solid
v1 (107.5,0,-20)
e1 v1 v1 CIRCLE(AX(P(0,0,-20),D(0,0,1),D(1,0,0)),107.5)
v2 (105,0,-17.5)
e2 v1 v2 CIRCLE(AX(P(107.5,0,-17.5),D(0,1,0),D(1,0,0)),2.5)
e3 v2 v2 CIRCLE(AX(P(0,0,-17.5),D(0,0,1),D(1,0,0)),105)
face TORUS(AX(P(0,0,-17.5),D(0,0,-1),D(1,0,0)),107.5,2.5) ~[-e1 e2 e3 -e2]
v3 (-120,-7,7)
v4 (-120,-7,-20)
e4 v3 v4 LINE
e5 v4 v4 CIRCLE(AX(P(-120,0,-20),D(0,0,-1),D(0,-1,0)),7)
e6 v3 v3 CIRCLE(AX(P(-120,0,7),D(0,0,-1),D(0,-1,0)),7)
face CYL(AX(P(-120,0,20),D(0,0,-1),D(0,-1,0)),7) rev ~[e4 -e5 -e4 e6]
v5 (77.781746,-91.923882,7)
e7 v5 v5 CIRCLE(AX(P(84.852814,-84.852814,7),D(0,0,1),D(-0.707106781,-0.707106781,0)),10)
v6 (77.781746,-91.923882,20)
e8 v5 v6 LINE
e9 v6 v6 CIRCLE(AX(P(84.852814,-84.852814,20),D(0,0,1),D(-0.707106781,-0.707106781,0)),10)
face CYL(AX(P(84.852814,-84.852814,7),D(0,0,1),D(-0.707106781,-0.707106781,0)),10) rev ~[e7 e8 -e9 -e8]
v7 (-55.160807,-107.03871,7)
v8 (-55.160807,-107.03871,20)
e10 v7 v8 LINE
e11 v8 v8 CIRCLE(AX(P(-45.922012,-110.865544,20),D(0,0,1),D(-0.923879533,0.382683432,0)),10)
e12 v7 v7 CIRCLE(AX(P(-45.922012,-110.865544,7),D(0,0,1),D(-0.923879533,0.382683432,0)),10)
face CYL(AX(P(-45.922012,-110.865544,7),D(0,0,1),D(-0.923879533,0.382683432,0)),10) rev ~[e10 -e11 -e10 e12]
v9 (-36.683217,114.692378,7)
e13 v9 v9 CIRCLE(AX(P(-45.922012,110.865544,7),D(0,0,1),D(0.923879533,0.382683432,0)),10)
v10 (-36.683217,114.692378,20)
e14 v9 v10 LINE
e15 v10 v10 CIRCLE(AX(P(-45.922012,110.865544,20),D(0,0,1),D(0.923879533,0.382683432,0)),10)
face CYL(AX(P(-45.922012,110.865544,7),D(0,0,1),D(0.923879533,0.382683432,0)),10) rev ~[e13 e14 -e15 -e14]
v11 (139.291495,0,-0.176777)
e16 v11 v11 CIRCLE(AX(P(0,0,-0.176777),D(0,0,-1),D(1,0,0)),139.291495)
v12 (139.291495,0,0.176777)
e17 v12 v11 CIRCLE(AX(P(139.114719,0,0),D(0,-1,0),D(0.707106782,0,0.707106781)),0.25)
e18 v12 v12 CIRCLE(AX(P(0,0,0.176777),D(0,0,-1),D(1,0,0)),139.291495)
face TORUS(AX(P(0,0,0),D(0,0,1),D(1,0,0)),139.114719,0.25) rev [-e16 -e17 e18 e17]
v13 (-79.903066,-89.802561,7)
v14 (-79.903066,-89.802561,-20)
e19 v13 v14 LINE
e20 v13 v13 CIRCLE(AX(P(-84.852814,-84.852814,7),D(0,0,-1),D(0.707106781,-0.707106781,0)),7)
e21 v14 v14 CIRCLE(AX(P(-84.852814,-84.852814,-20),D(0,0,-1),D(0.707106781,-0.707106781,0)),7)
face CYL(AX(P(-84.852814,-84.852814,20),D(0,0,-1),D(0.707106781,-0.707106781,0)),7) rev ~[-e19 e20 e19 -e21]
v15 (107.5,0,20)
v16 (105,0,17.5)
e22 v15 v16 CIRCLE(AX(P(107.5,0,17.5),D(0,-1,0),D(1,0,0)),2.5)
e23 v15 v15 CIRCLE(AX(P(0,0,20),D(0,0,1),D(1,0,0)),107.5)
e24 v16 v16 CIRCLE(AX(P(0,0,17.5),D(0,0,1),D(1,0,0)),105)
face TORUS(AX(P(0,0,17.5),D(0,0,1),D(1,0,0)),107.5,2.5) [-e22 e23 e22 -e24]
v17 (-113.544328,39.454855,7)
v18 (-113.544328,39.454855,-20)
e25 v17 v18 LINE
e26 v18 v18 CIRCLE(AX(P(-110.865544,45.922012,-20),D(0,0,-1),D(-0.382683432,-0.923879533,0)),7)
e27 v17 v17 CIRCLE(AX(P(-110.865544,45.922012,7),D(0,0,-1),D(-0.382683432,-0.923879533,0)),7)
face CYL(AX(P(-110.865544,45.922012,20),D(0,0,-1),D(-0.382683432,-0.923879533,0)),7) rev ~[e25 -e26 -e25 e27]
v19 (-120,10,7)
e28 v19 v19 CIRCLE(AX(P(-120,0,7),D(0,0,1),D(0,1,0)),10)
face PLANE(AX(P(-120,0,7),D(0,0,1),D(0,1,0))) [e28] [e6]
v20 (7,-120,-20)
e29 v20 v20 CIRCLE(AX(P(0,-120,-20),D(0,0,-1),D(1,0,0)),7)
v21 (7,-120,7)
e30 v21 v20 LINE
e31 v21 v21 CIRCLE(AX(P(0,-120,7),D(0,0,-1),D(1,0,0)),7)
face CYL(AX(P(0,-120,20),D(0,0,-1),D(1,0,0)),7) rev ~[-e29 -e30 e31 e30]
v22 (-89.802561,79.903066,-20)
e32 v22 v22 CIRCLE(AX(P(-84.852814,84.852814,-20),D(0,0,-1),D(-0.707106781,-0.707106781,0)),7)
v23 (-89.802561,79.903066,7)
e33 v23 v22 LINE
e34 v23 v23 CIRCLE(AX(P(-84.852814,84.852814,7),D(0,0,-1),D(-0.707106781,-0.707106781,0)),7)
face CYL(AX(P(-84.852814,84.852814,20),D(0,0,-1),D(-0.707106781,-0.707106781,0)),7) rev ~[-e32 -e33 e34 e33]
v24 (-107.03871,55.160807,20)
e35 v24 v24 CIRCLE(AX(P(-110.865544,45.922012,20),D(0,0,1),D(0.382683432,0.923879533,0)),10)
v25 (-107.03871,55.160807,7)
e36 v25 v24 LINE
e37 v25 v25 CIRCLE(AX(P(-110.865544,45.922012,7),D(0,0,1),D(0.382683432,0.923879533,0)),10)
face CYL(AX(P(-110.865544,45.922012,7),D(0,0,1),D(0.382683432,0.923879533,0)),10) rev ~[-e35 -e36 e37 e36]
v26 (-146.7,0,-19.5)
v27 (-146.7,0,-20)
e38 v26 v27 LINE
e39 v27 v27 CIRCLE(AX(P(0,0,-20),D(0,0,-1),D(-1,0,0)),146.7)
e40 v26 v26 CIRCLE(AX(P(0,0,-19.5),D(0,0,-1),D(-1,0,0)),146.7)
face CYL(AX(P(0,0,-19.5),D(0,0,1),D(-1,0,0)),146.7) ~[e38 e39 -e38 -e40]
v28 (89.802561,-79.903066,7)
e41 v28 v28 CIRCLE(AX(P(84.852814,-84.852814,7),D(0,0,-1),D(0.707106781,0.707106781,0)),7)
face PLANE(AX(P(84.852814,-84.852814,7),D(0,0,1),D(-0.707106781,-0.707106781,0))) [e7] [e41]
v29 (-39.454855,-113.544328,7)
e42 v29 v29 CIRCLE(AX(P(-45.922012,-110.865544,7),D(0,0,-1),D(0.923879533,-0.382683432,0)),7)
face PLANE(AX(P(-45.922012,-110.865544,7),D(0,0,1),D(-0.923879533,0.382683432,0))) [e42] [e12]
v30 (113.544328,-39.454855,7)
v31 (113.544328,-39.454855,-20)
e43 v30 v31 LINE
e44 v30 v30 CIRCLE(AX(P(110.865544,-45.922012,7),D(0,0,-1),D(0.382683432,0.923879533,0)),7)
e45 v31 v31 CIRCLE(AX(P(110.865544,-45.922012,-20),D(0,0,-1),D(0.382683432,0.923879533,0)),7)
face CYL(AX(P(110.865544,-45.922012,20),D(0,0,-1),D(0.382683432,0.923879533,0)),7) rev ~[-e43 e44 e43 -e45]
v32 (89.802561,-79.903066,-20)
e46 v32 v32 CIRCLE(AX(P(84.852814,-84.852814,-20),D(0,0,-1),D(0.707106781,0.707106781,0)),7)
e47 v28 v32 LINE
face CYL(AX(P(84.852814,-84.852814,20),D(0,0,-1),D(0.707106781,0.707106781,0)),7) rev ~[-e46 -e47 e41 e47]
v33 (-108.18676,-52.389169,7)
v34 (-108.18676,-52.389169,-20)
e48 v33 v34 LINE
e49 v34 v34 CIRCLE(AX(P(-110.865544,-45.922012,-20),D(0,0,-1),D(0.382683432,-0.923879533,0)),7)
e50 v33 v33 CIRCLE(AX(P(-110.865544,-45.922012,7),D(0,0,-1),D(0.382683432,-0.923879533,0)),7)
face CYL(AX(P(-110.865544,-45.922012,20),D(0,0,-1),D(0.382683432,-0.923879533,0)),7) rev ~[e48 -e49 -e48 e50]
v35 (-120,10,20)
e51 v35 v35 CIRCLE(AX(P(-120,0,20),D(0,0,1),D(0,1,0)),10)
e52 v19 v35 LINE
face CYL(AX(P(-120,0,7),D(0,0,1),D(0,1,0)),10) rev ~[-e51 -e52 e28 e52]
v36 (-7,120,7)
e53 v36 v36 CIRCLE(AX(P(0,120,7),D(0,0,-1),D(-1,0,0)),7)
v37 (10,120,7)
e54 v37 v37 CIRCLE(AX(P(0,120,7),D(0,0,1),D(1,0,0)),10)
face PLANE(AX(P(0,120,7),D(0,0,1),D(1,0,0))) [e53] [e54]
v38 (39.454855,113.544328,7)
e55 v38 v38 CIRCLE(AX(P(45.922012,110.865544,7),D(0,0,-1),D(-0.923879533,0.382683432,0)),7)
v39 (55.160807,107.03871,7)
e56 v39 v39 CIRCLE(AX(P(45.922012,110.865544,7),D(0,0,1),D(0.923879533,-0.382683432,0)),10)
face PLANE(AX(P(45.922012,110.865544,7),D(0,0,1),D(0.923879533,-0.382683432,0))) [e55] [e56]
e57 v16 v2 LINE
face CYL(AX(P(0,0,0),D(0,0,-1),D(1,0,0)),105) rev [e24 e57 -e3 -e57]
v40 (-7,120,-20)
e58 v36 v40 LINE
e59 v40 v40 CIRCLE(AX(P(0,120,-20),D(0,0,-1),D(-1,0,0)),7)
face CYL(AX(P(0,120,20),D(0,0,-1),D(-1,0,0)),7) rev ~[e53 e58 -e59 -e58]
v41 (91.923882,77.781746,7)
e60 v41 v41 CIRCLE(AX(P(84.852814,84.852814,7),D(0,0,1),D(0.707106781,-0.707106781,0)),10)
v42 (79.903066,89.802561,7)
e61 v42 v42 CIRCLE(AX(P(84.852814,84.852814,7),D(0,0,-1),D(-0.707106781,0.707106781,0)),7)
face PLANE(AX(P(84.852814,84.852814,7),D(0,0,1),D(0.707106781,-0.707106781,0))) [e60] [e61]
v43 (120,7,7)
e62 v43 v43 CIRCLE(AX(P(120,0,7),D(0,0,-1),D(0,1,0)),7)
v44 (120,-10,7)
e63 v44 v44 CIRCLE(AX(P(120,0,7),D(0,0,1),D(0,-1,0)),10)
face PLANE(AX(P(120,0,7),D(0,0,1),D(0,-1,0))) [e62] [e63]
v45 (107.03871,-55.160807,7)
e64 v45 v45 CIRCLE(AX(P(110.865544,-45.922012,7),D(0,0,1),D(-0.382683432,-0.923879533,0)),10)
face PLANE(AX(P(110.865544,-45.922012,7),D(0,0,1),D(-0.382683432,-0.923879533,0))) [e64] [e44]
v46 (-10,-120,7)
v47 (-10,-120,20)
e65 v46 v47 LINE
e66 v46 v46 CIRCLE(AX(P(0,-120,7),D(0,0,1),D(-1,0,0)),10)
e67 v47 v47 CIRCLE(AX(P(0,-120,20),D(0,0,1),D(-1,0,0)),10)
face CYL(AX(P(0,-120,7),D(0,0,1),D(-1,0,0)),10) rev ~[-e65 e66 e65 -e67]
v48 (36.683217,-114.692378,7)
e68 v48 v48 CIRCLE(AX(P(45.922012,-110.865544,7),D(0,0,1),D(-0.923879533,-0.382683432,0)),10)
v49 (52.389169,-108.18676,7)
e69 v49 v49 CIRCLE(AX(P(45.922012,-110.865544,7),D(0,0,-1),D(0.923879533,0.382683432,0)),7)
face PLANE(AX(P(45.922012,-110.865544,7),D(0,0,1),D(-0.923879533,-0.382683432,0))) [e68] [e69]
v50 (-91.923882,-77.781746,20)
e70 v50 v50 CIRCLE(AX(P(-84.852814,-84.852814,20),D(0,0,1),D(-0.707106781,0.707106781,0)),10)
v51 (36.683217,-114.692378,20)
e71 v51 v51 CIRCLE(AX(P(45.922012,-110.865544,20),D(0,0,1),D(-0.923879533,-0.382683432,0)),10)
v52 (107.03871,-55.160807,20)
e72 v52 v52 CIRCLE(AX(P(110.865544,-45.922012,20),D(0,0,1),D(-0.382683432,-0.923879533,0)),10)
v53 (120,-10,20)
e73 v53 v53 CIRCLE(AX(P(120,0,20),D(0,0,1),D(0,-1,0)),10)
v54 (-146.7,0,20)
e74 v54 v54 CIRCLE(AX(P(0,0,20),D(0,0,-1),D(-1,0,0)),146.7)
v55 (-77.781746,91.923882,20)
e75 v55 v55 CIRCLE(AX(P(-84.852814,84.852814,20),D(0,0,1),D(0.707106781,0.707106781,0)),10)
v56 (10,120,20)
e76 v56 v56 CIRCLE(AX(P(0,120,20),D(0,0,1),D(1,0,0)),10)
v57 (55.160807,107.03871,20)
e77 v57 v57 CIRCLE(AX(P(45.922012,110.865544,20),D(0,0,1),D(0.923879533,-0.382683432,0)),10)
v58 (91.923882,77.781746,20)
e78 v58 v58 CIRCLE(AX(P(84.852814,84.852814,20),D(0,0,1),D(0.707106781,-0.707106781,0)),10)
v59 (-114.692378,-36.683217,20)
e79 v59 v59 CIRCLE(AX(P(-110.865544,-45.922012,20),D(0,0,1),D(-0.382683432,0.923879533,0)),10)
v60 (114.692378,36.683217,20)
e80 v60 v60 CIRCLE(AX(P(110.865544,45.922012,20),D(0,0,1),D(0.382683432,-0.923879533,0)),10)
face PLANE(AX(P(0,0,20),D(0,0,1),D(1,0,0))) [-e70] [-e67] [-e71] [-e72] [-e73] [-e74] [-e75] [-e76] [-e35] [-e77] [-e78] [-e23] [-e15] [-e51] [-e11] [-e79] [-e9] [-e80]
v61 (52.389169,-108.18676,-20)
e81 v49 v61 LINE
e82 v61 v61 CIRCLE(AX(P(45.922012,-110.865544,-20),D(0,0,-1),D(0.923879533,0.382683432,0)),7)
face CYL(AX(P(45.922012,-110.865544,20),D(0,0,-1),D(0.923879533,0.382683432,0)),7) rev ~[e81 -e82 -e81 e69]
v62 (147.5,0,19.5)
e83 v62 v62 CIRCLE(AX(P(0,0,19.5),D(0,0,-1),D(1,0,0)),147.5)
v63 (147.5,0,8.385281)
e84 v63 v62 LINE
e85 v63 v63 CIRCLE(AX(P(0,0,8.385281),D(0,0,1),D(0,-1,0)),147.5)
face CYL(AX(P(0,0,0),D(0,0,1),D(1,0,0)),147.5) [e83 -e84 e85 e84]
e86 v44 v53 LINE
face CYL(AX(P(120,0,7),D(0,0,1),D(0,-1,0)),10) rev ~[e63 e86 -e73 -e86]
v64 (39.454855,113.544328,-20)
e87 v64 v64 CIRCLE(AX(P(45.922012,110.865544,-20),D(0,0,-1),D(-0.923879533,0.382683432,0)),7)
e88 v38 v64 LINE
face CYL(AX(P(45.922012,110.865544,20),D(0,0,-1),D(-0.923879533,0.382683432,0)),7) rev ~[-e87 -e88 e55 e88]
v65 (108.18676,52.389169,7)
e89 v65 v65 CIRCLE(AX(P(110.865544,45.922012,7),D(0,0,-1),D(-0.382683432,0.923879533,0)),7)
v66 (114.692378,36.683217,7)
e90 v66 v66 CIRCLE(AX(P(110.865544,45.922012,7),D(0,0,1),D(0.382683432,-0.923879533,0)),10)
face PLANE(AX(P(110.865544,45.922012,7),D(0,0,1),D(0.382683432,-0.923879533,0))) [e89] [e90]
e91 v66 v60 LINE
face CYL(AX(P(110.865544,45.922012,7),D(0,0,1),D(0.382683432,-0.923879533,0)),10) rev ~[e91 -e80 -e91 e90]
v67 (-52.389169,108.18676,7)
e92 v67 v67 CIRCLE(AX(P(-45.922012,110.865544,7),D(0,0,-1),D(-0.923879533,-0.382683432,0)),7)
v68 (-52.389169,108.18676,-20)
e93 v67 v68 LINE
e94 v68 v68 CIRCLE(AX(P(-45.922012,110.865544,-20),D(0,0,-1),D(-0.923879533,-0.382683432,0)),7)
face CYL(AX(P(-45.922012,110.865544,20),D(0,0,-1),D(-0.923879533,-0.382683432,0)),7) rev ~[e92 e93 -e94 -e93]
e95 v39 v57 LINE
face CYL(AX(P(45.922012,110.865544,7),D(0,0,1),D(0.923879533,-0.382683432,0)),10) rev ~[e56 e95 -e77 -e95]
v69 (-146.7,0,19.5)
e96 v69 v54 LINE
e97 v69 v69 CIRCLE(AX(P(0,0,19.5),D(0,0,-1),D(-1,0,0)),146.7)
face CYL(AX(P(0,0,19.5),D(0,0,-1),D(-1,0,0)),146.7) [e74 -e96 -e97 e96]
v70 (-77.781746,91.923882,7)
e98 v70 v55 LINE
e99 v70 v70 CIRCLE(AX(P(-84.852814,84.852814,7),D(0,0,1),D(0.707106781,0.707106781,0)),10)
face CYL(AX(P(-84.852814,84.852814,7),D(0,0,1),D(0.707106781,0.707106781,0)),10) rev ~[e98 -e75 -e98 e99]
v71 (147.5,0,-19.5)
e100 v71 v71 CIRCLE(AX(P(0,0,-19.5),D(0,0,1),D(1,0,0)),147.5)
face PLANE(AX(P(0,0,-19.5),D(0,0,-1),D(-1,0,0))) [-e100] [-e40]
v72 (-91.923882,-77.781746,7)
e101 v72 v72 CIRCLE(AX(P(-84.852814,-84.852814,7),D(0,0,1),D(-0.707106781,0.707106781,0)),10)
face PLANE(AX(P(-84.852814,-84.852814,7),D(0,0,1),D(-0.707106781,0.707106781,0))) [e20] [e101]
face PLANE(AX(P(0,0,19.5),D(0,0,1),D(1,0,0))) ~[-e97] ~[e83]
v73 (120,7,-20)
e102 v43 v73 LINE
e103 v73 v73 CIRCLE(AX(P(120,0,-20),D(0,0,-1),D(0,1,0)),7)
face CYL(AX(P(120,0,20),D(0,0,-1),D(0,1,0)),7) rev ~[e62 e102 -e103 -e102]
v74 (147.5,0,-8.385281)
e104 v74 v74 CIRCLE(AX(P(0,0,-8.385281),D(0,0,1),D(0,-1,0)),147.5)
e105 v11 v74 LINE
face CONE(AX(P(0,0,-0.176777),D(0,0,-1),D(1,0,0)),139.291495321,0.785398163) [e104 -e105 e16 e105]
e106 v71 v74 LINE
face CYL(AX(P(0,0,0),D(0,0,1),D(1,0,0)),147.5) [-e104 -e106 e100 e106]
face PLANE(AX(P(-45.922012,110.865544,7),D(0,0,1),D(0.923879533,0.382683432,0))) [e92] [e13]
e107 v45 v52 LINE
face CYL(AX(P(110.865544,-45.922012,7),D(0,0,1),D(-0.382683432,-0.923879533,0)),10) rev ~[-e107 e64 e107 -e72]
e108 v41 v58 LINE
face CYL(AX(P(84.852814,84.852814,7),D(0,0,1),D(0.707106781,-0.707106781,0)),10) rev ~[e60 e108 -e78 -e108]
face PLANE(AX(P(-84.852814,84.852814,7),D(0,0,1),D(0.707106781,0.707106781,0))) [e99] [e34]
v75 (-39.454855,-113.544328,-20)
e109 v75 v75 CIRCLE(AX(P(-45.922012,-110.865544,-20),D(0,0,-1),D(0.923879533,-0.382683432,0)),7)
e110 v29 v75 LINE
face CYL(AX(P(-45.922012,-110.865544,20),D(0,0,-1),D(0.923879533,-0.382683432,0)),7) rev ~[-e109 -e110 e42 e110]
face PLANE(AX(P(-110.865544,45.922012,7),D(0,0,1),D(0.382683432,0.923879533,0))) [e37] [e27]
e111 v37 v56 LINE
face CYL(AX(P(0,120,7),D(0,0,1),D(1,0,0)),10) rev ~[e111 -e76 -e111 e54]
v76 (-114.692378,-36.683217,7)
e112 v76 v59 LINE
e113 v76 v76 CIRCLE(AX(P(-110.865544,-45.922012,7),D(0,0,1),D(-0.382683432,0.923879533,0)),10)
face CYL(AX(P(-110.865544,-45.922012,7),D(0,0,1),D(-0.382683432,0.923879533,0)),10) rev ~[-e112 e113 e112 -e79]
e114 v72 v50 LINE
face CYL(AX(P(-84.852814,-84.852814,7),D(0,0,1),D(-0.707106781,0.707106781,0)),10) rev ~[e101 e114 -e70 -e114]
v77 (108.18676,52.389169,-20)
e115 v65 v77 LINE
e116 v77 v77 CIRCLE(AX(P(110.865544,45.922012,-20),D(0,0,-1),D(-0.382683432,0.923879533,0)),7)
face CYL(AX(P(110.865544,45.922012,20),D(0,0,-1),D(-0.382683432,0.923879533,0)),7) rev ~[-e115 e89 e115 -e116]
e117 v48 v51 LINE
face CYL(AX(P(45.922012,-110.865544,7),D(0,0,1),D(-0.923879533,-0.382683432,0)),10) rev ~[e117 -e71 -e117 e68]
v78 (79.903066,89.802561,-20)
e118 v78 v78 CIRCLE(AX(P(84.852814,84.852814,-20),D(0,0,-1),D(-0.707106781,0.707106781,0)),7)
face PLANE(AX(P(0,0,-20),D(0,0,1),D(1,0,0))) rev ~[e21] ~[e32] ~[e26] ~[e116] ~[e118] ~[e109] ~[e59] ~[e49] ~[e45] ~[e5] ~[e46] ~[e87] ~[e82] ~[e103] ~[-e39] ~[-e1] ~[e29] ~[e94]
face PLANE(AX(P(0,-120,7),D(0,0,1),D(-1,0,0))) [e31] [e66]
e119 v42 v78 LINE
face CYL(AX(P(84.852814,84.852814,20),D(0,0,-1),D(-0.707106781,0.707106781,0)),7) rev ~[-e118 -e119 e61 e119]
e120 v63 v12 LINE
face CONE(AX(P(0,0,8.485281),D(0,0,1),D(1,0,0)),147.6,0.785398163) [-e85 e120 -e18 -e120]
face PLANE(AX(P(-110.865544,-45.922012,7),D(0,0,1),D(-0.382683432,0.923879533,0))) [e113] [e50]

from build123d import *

# Parameters (mm, degrees)
SKETCH_1_R                = 147.5
SKETCH_1_R_2              = 105
EXTRUDE_1_DEPTH           = 20
HOLE_WIZARD_2_D           = 14
HOLE_WIZARD_2_CBORE_D     = 20
HOLE_WIZARD_2_CBORE_DEPTH = 13
PATTERN_CIRCULAR_1_COUNT  = 16
CUT_EXTRUDE_START         = -0.5
SKETCH_6_R                = 147.5
SKETCH_6_R_2              = 146.7
CUT_EXTRUDE_1_DEPTH       = 0.5
FILLET_1_R                = 2.5


with BuildPart() as part:
    # 草图1 → 凸台-拉伸1 (new, symmetric)
    with BuildSketch(Plane.XY):
        Circle(SKETCH_1_R)
        Circle(SKETCH_1_R_2, mode=Mode.SUBTRACT)
    extrude(amount=EXTRUDE_1_DEPTH, both=True)

    # 打孔尺寸(%根据)内六角圆柱头螺钉的类型2 (through all)
    with Locations(Plane.XY.offset(20)):
        with Locations((0, 120)):
            hole_wizard_2 = CounterBoreHole(HOLE_WIZARD_2_D / 2, HOLE_WIZARD_2_CBORE_D / 2, HOLE_WIZARD_2_CBORE_DEPTH)

    # 阵列(圆周)1: 打孔尺寸(%根据)内六角圆柱头螺钉的类型2 ×16 about axis
    pattern_circular_1_axis = Axis((0, 0, 0), (0, 0, 1))
    for i in range(1, PATTERN_CIRCULAR_1_COUNT):
        add(hole_wizard_2.rotate(pattern_circular_1_axis, i * 360 / PATTERN_CIRCULAR_1_COUNT), mode=Mode.SUBTRACT)

    # 草图5 → 切除-旋转1 (revolve, cut)
    with BuildSketch(Plane(origin=(0, 0, 0), x_dir=(1, 0, 0), z_dir=(0, 1, 0))):
        with BuildLine():
            Line((139.291495321, 0.176776695), (147.6, 8.485281374))
            Line((147.6, 8.485281374), (147.6, -8.485281374))
            Line((147.6, -8.485281374), (139.291495321, -0.176776695))
            ThreePointArc((139.291495321, -0.176776695), (138.864718626, 0), (139.291495321, 0.176776695))
        make_face()
    revolve(axis=Axis((0, 0, 20), (0, 0, -1)), mode=Mode.SUBTRACT)

    # 草图6 → 切除-拉伸1 (cut)
    with BuildSketch(Plane(origin=(0, 0, -20), x_dir=(-1, 0, 0), z_dir=(0, 0, -1)).offset(CUT_EXTRUDE_START)):
        Circle(SKETCH_6_R)
        Circle(SKETCH_6_R_2, mode=Mode.SUBTRACT)
    cut_extrude_1 = extrude(amount=CUT_EXTRUDE_1_DEPTH, mode=Mode.SUBTRACT)

    # 镜向1: 切除-拉伸1 across plane
    add(cut_extrude_1.mirror(Plane.XY), mode=Mode.SUBTRACT)

    # 圆角1
    fillet_1_edges = [part.edges().sort_by_distance(p)[0] for p in [
        (-105, 0, -20),
        (-105, 0, 20),
    ]]
    fillet(fillet_1_edges, radius=FILLET_1_R)


solid = part.part
